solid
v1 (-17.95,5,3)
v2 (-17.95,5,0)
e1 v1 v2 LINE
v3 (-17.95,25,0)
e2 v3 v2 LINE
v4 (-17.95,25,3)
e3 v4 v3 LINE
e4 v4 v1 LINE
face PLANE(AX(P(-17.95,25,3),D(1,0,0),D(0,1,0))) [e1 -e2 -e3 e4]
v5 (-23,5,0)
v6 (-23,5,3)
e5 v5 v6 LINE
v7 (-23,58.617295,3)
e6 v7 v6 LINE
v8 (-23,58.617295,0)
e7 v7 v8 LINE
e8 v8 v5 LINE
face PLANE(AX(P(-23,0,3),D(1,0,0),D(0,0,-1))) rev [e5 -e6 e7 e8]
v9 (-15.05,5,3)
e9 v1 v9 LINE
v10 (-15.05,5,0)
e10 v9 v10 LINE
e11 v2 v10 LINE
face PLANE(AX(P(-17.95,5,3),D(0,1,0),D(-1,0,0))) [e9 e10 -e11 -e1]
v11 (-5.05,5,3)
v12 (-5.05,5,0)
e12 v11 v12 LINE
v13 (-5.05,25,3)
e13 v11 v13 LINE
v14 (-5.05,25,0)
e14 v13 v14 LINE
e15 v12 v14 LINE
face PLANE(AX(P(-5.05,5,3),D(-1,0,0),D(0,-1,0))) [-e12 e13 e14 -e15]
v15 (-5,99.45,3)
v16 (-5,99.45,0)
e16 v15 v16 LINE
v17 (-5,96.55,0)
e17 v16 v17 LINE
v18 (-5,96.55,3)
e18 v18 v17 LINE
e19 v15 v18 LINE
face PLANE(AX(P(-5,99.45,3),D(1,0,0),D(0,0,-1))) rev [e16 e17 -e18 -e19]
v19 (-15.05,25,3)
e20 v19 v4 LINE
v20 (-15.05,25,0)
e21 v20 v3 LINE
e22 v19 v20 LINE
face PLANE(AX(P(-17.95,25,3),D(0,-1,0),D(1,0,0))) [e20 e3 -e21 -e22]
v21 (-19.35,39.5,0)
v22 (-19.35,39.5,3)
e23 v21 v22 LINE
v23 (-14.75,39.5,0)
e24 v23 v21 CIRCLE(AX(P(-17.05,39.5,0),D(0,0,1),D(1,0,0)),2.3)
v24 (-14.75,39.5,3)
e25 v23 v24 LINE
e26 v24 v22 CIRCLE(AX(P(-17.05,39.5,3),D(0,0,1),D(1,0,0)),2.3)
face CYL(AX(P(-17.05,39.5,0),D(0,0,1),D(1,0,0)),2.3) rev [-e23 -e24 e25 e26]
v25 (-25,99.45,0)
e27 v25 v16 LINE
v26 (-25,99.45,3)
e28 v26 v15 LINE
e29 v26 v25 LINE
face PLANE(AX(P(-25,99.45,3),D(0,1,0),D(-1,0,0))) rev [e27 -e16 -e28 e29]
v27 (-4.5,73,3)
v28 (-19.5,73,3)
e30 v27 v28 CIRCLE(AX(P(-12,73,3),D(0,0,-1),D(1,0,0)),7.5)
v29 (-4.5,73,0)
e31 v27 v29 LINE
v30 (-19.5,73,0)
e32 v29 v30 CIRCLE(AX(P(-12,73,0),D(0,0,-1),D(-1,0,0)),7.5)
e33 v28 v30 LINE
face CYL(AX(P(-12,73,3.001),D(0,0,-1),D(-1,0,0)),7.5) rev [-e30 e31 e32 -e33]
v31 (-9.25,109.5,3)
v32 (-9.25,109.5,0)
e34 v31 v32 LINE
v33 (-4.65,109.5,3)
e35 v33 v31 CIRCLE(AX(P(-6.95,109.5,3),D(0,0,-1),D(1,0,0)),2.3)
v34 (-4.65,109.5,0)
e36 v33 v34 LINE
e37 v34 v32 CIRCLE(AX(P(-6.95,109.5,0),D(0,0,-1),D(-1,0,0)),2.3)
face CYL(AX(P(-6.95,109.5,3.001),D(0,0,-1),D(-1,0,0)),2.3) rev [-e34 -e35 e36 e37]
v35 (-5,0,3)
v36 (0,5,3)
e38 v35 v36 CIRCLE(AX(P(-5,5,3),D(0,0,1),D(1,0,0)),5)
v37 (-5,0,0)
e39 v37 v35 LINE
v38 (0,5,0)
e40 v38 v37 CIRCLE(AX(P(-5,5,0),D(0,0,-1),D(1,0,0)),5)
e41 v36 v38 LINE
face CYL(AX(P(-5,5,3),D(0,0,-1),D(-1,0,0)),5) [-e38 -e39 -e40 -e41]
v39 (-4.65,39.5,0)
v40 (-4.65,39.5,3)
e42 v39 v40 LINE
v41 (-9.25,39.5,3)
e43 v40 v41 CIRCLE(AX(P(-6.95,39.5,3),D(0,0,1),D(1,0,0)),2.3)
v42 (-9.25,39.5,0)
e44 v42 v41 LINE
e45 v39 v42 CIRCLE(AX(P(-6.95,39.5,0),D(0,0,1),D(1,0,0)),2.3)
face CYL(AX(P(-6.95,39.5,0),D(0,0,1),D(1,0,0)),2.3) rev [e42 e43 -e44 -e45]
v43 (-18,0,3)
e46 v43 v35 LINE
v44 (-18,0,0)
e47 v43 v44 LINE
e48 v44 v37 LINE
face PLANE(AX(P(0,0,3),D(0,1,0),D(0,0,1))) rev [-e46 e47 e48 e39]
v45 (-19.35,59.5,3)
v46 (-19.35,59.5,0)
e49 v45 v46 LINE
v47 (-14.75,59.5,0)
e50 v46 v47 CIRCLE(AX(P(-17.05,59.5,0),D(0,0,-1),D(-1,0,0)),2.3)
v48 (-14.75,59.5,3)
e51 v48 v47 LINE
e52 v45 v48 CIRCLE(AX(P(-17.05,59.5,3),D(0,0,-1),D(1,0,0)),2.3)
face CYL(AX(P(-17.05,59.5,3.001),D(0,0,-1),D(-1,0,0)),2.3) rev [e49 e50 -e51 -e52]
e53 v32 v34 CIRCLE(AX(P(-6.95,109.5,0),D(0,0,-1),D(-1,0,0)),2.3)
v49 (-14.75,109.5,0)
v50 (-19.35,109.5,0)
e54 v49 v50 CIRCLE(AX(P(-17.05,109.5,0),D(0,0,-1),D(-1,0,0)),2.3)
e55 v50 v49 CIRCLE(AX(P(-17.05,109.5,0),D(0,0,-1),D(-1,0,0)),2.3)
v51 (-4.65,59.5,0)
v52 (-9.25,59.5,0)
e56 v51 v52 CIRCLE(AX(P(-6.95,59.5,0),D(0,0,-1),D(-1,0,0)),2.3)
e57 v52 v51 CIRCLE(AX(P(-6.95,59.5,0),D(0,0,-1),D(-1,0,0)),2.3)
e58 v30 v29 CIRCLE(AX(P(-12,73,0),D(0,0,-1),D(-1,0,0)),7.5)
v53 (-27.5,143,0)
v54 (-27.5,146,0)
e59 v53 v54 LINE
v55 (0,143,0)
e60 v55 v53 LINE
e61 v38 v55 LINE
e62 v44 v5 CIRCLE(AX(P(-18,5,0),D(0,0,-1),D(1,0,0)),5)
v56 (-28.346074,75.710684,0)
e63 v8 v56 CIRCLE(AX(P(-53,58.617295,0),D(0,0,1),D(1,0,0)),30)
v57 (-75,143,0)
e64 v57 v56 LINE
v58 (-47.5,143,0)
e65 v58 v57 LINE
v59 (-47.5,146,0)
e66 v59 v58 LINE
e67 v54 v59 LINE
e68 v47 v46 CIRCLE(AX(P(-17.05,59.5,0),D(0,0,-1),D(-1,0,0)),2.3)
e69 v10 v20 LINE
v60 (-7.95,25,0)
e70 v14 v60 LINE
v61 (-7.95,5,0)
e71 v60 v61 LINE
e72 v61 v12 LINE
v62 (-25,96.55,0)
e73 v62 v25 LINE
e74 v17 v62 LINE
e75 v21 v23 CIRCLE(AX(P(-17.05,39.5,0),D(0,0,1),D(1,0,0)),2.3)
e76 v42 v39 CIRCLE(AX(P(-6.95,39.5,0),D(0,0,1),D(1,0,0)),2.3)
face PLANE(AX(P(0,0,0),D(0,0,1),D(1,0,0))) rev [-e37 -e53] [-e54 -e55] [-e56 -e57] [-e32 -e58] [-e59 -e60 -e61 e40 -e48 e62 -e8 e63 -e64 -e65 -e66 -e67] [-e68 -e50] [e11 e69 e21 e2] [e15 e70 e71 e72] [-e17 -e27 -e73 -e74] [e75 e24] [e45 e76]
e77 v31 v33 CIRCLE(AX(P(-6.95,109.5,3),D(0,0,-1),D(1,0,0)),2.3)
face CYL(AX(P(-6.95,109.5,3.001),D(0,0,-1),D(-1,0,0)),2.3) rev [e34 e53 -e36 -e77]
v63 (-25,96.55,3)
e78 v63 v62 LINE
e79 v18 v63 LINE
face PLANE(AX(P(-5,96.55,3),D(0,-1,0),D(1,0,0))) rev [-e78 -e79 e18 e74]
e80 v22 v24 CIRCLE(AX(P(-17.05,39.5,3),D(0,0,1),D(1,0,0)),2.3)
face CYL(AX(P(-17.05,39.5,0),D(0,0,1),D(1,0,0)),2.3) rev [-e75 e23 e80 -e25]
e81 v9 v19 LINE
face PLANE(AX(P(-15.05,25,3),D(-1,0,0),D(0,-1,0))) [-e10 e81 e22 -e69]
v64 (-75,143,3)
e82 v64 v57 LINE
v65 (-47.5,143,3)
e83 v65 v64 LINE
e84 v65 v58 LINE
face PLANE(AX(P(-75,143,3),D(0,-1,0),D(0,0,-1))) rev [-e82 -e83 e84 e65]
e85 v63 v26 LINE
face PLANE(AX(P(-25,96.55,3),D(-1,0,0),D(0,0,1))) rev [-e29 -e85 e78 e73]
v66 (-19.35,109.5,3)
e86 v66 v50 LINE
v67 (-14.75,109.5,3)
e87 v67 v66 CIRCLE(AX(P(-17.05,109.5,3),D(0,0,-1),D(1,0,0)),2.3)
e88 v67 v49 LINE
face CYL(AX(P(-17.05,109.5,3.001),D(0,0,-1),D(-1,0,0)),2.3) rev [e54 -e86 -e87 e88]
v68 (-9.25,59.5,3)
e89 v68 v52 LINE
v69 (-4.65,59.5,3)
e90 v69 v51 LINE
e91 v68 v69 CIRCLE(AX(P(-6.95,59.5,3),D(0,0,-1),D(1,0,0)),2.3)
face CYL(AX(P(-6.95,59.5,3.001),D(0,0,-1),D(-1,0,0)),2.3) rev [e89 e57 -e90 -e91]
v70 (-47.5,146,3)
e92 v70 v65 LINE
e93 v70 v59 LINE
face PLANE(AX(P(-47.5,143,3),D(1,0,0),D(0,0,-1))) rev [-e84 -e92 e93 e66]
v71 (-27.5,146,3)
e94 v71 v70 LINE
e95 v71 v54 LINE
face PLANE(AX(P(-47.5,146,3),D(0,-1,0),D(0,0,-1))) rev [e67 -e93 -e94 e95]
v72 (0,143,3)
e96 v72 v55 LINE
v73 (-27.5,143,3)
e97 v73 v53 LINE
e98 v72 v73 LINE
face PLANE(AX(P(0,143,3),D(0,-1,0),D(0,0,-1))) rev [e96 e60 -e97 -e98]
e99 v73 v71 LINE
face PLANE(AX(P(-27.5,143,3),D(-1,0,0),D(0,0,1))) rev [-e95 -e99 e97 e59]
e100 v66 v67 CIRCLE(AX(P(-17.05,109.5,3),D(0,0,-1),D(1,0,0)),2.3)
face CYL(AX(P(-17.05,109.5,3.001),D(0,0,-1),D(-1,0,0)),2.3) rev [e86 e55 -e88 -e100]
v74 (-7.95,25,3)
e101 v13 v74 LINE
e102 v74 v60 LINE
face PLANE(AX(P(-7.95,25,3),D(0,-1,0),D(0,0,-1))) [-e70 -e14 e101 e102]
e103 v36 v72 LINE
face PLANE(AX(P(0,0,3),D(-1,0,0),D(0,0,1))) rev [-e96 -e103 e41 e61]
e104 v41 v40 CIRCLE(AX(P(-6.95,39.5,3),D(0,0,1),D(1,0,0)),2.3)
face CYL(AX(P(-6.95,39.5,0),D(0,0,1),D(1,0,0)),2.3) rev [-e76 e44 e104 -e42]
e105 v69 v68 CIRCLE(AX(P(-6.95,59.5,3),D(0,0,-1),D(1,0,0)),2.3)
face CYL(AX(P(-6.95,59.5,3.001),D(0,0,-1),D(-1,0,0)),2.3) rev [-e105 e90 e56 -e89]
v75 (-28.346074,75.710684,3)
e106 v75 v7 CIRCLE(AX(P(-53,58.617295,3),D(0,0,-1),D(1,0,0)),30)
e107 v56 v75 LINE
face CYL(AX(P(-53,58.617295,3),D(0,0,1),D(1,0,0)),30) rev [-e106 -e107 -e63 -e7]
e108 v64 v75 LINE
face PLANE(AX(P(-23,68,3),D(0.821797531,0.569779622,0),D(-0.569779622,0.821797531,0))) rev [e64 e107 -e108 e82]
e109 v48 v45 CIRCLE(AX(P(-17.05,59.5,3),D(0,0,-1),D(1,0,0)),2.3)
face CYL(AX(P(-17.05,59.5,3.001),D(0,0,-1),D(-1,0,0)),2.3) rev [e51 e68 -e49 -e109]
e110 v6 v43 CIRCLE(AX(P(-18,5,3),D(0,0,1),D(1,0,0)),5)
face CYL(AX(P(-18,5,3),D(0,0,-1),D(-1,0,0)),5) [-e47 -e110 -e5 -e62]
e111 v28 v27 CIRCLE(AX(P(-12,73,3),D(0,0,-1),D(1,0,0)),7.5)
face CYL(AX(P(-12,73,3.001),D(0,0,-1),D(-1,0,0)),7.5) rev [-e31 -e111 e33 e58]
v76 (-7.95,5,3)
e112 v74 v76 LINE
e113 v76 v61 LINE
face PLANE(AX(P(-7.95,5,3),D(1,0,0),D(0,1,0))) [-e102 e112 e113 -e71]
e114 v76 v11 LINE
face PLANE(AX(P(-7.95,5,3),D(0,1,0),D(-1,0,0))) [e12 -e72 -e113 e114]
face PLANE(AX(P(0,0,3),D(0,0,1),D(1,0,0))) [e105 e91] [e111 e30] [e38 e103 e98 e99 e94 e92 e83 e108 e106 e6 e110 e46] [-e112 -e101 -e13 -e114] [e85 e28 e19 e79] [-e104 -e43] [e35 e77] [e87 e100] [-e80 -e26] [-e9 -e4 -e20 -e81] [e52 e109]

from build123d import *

# Parameters (mm, degrees)
SKETCH1_W           = 2.9
SKETCH1_H           = 20
BOSS_EXTRUDE1_DEPTH = 3
FILLET1_R           = 5
FILLET2_R           = 30
CUT_EXTRUDE1_REACH  = 166.165
SKETCH3_R           = 7.5
SKETCH3_R_2         = 2.3
SKETCH5_W           = 20
SKETCH5_H           = 2.9
CUT_EXTRUDE2_DEPTH  = 3
SKETCH6_R           = 2.3
CUT_EXTRUDE3_DEPTH  = 3


with BuildPart() as part:
    # Sketch1 → Boss-Extrude1 (new body)
    with BuildSketch(Plane.XY):
        Polygon((0, 0), (-23, 0), (-23, 68), (-75, 143), (-47.5, 143), (-47.5, 146), (-27.5, 146), (-27.5, 143), (0, 143), align=None)
        with Locations((-16.5, 15)):
            Rectangle(SKETCH1_W, SKETCH1_H, mode=Mode.SUBTRACT)
        with Locations((-6.5, 15)):
            Rectangle(SKETCH1_W, SKETCH1_H, mode=Mode.SUBTRACT)
    extrude(amount=BOSS_EXTRUDE1_DEPTH)

    # Fillet1
    fillet1_edges = [part.edges().sort_by_distance(p)[0] for p in [
        (0, 0, 1.5),
        (-23, 0, 1.5),
    ]]
    fillet(fillet1_edges, radius=FILLET1_R)

    # Fillet2
    fillet2_edges = [part.edges().sort_by_distance(p)[0] for p in [
        (-23, 68, 1.5),
    ]]
    fillet(fillet2_edges, radius=FILLET2_R)

    # Sketch3 → Cut-Extrude1 (cut, up to next)
    with BuildSketch(Plane(origin=(0, 0, 0), x_dir=(-1, 0, 0), z_dir=(0, 0, -1)), mode=Mode.PRIVATE) as cut_extrude1_sk1:
        with Locations((12, 73)):
            Circle(SKETCH3_R)
    cut_extrude1_tool1 = extrude(cut_extrude1_sk1.sketch, amount=-CUT_EXTRUDE1_REACH, mode=Mode.PRIVATE) & part.part
    # Sketch3 → Cut-Extrude1 (cut, up to next)
    with BuildSketch(Plane(origin=(0, 0, 0), x_dir=(-1, 0, 0), z_dir=(0, 0, -1)), mode=Mode.PRIVATE) as cut_extrude1_sk2:
        with Locations((17.05, 59.5)):
            Circle(SKETCH3_R_2)
    cut_extrude1_tool2 = extrude(cut_extrude1_sk2.sketch, amount=-CUT_EXTRUDE1_REACH, mode=Mode.PRIVATE) & part.part
    # Sketch3 → Cut-Extrude1 (cut, up to next)
    with BuildSketch(Plane(origin=(0, 0, 0), x_dir=(-1, 0, 0), z_dir=(0, 0, -1)), mode=Mode.PRIVATE) as cut_extrude1_sk3:
        with Locations((6.95, 59.5)):
            Circle(SKETCH3_R_2)
    cut_extrude1_tool3 = extrude(cut_extrude1_sk3.sketch, amount=-CUT_EXTRUDE1_REACH, mode=Mode.PRIVATE) & part.part
    # Sketch3 → Cut-Extrude1 (cut, up to next)
    with BuildSketch(Plane(origin=(0, 0, 0), x_dir=(-1, 0, 0), z_dir=(0, 0, -1)), mode=Mode.PRIVATE) as cut_extrude1_sk4:
        with Locations((17.05, 109.5)):
            Circle(SKETCH3_R_2)
    cut_extrude1_tool4 = extrude(cut_extrude1_sk4.sketch, amount=-CUT_EXTRUDE1_REACH, mode=Mode.PRIVATE) & part.part
    # Sketch3 → Cut-Extrude1 (cut, up to next)
    with BuildSketch(Plane(origin=(0, 0, 0), x_dir=(-1, 0, 0), z_dir=(0, 0, -1)), mode=Mode.PRIVATE) as cut_extrude1_sk5:
        with Locations((6.95, 109.5)):
            Circle(SKETCH3_R_2)
    cut_extrude1_tool5 = extrude(cut_extrude1_sk5.sketch, amount=-CUT_EXTRUDE1_REACH, mode=Mode.PRIVATE) & part.part
    add(cut_extrude1_tool1.solids().sort_by_distance((-12, 73, 0))[0], mode=Mode.SUBTRACT)
    add(cut_extrude1_tool2.solids().sort_by_distance((-17.05, 59.5, 0))[0], mode=Mode.SUBTRACT)
    add(cut_extrude1_tool3.solids().sort_by_distance((-6.95, 59.5, 0))[0], mode=Mode.SUBTRACT)
    add(cut_extrude1_tool4.solids().sort_by_distance((-17.05, 109.5, 0))[0], mode=Mode.SUBTRACT)
    add(cut_extrude1_tool5.solids().sort_by_distance((-6.95, 109.5, 0))[0], mode=Mode.SUBTRACT)

    # Sketch5 → Cut-Extrude2 (cut)
    with BuildSketch(Plane(origin=(0, 0, 0), x_dir=(-1, 0, 0), z_dir=(0, 0, -1))):
        with Locations((15, 98)):
            Rectangle(SKETCH5_W, SKETCH5_H)
    extrude(amount=-CUT_EXTRUDE2_DEPTH, mode=Mode.SUBTRACT)

    # Sketch6 → Cut-Extrude3 (cut)
    with BuildSketch(Plane.XY.offset(3)):
        with Locations((-17.05, 39.5)):
            Circle(SKETCH6_R)
        with Locations((-6.95, 39.5)):
            Circle(SKETCH6_R)
    extrude(amount=-CUT_EXTRUDE3_DEPTH, mode=Mode.SUBTRACT)


solid = part.part
